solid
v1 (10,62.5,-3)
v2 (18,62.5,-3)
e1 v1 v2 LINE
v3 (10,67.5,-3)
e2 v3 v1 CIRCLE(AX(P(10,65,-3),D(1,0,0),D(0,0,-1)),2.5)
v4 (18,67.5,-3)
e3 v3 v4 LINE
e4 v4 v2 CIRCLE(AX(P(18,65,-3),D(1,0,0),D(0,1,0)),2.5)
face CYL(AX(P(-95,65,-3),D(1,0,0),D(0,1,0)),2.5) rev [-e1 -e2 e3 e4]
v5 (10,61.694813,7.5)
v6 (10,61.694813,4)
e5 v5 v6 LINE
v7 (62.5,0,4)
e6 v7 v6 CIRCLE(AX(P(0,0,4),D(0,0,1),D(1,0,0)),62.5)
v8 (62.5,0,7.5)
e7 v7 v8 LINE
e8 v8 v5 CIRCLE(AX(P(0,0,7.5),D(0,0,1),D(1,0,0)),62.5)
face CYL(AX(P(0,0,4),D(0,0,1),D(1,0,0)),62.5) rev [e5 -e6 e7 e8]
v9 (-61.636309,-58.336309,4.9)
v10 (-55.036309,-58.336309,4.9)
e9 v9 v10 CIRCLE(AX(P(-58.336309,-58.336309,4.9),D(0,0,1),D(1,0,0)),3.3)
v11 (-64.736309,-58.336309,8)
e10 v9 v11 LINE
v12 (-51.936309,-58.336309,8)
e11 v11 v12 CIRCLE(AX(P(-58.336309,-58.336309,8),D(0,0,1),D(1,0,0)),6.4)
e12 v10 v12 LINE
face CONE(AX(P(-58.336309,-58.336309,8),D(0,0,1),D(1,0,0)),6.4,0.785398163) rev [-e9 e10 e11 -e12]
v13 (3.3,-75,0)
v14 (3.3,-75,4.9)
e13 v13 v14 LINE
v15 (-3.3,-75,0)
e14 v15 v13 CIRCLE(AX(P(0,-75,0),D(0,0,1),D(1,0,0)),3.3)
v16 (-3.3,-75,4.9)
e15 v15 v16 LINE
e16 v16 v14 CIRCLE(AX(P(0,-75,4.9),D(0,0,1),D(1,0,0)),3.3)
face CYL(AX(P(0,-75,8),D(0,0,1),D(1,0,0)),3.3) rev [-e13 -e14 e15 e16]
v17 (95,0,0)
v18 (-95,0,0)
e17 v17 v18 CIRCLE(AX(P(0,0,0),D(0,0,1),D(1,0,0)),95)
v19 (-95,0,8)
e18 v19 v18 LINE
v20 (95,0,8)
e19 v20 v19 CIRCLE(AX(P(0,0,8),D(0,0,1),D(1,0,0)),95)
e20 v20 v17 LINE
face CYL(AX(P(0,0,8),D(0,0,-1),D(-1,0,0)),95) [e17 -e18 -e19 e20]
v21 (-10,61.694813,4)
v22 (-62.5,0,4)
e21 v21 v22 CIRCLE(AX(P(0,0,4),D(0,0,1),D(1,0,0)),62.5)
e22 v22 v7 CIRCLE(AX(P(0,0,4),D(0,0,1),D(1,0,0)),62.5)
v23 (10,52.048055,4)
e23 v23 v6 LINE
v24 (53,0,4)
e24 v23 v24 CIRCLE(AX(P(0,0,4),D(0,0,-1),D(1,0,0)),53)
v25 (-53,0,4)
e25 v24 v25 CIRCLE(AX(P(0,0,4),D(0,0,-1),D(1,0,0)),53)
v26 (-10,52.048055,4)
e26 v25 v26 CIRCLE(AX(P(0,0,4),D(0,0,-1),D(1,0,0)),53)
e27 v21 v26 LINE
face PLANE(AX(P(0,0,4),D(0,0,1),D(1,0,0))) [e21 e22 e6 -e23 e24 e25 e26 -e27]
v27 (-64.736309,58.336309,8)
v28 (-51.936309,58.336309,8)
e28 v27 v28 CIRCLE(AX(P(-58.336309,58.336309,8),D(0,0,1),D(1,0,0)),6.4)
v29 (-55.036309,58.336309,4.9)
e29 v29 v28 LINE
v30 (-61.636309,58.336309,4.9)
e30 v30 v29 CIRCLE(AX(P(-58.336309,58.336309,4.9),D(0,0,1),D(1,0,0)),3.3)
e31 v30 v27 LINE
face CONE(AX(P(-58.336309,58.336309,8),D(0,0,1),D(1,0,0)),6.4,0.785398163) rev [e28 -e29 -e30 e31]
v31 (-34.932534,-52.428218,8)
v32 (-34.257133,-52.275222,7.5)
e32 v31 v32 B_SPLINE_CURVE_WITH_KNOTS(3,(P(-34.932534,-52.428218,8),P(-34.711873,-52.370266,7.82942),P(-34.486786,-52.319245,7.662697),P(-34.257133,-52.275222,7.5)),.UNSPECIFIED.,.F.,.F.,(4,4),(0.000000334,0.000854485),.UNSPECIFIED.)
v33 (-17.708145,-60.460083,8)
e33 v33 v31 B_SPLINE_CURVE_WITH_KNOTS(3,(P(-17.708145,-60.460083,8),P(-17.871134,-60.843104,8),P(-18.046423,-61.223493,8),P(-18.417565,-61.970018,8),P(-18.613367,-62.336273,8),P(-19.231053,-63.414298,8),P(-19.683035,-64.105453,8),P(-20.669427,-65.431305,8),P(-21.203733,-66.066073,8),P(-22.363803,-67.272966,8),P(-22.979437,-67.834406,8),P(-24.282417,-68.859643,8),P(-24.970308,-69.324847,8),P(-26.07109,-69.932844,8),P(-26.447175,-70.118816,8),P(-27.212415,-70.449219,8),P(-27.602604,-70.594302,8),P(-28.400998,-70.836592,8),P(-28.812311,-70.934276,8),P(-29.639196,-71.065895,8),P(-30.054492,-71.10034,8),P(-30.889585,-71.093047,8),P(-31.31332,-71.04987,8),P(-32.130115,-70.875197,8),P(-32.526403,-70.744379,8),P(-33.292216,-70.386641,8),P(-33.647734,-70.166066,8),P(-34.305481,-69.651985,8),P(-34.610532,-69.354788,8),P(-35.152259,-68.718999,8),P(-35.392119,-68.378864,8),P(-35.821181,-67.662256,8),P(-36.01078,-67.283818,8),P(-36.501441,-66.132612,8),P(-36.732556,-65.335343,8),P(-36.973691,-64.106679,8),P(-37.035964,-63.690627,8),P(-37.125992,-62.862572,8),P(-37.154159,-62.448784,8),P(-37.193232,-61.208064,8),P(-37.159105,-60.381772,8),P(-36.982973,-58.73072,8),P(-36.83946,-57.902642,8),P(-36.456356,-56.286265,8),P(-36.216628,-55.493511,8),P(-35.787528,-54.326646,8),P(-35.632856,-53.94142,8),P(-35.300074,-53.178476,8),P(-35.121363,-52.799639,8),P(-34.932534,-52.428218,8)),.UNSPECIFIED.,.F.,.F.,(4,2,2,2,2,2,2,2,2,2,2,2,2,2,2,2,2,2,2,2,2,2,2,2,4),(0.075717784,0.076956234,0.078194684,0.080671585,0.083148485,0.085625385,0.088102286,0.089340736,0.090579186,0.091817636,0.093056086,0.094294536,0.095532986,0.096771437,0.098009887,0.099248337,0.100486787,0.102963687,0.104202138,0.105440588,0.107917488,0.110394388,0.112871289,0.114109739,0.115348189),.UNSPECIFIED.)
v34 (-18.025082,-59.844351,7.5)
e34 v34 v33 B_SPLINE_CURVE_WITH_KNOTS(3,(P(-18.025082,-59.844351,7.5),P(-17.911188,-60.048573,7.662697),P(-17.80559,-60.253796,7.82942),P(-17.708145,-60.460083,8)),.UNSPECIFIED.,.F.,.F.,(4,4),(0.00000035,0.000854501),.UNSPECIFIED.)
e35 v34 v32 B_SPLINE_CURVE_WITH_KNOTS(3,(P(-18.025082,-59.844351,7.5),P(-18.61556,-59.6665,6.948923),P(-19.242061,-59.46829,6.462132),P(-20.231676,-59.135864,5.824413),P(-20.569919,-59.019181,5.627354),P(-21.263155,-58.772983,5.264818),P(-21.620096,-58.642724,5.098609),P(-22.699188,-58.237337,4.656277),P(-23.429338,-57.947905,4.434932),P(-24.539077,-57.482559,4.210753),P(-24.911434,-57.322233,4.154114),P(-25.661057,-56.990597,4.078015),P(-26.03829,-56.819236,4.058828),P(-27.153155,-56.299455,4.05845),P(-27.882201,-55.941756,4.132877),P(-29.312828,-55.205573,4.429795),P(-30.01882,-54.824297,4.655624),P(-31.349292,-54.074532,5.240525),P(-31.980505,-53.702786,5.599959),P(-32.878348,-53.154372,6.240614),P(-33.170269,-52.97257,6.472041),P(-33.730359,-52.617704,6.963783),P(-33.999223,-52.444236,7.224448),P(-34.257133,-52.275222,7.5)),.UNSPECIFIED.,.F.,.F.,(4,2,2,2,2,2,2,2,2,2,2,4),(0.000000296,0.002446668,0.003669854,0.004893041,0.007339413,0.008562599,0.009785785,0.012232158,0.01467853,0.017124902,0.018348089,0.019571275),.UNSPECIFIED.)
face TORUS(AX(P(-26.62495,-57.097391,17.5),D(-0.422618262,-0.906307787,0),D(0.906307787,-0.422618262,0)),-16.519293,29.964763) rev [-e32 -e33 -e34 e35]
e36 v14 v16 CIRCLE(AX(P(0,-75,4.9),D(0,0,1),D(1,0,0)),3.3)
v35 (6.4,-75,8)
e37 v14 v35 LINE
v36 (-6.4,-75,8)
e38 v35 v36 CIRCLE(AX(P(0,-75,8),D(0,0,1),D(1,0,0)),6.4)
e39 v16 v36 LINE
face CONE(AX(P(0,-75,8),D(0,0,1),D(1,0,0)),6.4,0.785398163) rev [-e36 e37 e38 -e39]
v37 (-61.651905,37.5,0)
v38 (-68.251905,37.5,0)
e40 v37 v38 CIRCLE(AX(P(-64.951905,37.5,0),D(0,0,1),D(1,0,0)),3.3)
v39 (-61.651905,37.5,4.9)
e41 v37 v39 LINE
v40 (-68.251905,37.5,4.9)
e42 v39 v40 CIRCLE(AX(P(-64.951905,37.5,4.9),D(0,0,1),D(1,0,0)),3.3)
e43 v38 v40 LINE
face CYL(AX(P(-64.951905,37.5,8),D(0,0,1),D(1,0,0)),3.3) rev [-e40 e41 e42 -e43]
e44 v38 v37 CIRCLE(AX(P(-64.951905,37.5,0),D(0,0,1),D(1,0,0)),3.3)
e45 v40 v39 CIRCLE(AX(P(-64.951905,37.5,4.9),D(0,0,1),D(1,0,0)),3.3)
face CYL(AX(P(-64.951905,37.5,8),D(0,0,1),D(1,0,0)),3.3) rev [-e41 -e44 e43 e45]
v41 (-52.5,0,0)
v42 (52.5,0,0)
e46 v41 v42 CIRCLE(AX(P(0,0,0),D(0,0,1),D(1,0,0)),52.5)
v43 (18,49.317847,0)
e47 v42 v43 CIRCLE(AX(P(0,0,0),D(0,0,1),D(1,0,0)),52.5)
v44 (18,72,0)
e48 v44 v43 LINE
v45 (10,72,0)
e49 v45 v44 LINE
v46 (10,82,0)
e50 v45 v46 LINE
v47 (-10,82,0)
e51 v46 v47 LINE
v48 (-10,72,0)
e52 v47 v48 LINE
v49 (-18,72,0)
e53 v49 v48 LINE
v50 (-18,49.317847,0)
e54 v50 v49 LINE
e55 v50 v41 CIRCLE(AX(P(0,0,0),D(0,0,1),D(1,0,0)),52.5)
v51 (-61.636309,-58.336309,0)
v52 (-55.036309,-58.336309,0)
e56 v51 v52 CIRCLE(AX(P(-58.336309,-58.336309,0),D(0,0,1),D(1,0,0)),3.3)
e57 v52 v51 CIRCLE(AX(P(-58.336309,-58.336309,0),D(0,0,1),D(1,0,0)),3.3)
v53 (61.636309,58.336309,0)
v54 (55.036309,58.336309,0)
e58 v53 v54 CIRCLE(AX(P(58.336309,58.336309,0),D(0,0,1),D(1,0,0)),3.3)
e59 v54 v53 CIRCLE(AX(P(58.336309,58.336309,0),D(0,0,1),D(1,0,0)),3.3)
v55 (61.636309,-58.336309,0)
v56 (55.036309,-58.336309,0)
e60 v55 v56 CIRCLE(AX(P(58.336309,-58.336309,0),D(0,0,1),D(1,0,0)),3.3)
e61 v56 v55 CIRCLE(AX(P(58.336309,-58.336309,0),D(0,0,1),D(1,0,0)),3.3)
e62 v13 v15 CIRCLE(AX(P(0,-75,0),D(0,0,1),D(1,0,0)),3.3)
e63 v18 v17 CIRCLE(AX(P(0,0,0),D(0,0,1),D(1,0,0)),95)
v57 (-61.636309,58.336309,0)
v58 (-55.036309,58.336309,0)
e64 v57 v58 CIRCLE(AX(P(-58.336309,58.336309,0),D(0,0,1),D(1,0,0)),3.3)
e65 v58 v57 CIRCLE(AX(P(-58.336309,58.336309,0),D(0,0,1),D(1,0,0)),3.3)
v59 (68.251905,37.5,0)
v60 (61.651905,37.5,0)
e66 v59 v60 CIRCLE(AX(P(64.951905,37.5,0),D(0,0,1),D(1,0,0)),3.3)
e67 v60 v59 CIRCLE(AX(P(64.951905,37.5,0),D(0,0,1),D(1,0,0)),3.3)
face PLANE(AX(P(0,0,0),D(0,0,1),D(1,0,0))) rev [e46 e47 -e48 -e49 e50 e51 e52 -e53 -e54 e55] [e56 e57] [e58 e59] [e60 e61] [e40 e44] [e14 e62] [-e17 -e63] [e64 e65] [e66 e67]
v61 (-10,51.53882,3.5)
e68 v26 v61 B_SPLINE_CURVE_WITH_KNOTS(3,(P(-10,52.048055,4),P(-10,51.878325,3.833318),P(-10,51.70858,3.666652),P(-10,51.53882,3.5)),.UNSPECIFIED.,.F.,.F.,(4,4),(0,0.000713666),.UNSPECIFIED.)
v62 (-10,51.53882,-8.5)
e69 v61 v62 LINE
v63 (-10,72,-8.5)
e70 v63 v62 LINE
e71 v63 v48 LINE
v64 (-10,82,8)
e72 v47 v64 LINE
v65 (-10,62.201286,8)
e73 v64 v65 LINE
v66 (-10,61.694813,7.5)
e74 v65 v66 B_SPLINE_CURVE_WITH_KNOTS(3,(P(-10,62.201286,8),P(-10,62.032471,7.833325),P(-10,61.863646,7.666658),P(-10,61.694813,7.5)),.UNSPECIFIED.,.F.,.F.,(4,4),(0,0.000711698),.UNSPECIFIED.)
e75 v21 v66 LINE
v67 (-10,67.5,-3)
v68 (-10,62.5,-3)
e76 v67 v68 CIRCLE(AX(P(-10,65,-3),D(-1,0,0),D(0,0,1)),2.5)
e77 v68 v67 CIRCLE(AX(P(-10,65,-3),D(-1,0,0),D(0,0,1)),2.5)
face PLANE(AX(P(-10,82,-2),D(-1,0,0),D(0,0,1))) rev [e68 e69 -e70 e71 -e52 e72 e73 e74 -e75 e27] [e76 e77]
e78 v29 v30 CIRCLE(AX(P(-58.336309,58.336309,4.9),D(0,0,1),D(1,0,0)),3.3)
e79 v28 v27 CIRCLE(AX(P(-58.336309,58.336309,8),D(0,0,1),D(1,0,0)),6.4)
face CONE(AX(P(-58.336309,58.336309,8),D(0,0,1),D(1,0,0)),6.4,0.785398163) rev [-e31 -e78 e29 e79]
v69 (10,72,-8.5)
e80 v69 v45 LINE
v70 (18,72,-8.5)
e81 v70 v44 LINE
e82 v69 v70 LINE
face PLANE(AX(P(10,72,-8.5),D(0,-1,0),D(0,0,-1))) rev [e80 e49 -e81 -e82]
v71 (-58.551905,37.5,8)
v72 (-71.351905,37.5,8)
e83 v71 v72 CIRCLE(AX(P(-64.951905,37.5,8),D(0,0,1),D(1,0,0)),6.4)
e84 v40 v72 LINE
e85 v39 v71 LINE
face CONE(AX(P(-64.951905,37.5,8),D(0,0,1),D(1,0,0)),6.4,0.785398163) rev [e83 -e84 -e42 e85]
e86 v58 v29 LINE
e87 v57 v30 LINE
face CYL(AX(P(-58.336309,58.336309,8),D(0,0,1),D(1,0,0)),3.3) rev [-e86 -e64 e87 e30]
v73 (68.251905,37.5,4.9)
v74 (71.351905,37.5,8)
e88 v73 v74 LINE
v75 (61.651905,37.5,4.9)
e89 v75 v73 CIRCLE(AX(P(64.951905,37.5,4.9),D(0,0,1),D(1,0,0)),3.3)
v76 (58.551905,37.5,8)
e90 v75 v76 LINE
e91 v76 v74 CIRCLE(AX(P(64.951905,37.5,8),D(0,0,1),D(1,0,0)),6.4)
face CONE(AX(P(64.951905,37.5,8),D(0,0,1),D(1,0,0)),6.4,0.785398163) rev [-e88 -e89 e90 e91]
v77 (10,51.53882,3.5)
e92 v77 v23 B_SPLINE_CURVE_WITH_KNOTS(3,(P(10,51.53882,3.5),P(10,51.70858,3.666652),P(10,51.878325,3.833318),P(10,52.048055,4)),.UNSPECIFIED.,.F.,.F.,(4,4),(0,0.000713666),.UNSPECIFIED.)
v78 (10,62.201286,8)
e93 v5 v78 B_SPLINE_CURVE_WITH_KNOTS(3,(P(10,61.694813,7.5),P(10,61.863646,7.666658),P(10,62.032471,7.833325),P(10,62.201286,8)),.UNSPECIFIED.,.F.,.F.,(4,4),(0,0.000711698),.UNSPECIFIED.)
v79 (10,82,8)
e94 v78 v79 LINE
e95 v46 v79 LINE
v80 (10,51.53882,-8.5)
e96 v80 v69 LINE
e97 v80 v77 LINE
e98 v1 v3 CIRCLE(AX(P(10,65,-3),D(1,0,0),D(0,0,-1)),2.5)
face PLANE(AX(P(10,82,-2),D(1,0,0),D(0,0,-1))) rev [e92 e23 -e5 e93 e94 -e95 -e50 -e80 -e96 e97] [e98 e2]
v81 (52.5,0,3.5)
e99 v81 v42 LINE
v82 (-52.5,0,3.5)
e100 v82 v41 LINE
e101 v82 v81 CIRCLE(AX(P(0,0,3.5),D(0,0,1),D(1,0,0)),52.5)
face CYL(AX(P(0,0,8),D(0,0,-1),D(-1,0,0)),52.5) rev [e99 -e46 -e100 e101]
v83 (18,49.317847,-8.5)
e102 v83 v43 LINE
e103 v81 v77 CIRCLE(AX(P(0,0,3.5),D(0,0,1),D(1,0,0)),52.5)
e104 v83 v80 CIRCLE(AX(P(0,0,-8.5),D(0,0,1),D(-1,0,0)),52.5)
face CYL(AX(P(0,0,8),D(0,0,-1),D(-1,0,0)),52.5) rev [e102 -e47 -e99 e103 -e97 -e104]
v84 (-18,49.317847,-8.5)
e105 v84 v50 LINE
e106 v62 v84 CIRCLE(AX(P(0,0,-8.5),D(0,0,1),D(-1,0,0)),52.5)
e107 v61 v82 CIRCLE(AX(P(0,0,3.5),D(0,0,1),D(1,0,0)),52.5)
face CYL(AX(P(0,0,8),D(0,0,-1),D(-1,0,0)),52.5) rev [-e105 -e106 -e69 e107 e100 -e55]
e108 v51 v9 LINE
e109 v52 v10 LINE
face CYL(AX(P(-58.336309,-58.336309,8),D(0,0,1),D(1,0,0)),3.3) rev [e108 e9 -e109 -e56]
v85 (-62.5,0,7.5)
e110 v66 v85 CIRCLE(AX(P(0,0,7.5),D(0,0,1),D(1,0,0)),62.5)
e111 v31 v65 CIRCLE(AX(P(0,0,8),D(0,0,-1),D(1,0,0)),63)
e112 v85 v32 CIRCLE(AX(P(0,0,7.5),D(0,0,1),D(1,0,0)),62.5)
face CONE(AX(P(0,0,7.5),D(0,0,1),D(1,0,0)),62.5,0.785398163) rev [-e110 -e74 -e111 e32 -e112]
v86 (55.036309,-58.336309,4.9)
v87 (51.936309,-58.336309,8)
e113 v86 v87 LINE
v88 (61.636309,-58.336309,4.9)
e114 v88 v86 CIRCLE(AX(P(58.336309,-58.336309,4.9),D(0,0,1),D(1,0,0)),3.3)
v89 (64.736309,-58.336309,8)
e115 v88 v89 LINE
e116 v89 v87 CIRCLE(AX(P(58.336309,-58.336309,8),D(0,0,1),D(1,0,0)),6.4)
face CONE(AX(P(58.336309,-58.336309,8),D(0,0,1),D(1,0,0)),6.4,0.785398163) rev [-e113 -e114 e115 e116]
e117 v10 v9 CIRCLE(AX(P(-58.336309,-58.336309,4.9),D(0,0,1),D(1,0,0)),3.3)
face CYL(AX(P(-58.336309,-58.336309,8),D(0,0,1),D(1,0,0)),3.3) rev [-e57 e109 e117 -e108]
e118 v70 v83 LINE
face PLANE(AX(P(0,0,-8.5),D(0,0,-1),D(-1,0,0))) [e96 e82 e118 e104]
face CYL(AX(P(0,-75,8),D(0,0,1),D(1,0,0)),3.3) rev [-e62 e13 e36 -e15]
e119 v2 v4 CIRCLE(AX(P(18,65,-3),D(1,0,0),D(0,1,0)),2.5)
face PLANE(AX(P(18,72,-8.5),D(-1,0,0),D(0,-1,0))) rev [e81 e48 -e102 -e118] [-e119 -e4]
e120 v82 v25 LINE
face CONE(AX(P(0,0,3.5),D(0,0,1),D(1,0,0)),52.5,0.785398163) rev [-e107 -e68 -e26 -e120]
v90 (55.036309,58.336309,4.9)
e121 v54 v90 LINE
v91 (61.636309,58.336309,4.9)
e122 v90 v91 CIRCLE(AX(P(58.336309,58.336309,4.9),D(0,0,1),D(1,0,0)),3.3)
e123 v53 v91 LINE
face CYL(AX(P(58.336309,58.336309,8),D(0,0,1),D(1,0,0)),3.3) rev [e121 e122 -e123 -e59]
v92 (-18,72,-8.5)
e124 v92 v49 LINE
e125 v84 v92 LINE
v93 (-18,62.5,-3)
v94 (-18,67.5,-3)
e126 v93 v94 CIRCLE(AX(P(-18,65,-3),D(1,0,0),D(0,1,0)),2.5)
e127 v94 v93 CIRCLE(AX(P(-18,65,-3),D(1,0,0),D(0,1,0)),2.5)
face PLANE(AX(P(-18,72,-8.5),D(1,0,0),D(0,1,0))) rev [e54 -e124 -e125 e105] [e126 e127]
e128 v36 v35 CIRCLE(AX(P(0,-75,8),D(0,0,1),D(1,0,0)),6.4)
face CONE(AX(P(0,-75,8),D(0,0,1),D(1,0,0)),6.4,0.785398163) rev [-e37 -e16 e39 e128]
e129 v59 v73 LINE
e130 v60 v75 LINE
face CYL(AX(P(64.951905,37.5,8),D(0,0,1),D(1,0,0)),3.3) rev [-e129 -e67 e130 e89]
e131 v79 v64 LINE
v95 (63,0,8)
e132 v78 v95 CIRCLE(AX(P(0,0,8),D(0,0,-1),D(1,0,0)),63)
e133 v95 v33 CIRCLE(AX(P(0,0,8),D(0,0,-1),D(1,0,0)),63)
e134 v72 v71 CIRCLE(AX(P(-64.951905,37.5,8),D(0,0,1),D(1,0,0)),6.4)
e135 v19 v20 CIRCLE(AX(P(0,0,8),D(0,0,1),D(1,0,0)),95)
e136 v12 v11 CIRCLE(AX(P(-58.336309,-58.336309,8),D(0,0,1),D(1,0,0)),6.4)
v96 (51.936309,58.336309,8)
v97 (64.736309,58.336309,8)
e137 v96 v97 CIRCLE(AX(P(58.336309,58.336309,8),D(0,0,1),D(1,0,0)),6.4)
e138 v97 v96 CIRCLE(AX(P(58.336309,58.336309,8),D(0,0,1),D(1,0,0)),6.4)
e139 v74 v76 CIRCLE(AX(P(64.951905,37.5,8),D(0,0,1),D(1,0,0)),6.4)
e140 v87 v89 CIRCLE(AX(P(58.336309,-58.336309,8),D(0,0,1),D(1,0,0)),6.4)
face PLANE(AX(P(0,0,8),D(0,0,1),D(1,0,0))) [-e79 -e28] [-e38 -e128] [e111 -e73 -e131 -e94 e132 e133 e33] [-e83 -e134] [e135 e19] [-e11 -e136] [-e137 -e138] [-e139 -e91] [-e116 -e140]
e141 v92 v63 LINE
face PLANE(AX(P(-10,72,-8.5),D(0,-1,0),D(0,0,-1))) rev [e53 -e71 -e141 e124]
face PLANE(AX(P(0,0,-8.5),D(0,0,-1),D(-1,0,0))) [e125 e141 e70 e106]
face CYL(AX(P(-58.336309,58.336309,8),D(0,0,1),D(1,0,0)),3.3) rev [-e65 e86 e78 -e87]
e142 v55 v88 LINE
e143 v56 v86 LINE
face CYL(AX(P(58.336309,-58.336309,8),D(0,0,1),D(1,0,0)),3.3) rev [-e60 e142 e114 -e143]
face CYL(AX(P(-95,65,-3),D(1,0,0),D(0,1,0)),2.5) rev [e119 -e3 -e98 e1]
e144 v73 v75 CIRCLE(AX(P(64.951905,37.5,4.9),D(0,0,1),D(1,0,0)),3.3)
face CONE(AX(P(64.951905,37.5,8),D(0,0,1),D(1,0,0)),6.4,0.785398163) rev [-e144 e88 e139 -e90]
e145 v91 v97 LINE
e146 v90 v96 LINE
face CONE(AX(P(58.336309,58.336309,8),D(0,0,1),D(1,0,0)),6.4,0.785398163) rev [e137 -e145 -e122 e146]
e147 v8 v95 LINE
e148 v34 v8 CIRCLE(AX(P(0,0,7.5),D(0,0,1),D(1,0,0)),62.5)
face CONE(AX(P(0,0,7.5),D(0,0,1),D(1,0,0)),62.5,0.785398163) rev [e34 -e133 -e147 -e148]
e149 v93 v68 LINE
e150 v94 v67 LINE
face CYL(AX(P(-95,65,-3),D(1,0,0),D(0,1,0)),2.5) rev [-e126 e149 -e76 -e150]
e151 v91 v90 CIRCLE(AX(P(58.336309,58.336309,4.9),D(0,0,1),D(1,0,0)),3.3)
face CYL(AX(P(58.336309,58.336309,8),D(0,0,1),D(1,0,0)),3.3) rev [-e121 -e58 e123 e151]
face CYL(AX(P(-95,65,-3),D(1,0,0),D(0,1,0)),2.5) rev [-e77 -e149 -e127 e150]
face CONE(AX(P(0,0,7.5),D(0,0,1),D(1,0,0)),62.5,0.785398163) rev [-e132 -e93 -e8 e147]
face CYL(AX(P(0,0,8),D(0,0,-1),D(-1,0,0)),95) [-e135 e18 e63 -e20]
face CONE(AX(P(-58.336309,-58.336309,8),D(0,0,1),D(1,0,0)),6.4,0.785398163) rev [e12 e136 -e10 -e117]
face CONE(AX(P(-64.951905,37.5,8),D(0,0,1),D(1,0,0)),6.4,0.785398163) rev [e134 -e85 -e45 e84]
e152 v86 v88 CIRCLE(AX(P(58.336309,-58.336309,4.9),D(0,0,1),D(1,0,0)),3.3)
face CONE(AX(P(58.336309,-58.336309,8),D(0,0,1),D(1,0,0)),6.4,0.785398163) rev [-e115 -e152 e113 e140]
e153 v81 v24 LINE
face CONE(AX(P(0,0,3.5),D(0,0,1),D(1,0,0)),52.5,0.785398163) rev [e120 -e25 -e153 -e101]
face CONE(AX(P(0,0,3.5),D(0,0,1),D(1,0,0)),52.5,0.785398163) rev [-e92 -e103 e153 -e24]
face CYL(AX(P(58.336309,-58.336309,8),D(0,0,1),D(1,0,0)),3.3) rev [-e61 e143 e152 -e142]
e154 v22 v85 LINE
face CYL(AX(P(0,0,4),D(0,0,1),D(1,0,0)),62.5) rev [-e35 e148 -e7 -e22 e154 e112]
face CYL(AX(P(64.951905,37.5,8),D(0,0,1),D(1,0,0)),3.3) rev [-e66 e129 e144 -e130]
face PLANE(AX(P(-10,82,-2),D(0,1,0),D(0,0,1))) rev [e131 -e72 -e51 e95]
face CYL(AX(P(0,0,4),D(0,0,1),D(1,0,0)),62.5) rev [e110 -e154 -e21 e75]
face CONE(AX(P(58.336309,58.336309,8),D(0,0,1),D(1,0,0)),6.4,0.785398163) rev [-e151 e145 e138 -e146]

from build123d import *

# Parameters (mm, degrees)
SKETCH_1_R               = 95
SKETCH_1_R_2             = 52.5
EXTRUDE_1_DEPTH          = 8
SKETCH_3_R               = 62.5
CUT_EXTRUDE_1_DEPTH      = 4
PATTERN_CIRCULAR_1_COUNT = 3
PATTERN_CIRCULAR_2_COUNT = 4
SKETCH_7_W               = 20
SKETCH_7_H               = 39
CUT_EXTRUDE_2_DEPTH      = 10
EXTRUDE_START            = 8.5
EXTRUDE_2_DEPTH          = 8.5
SKETCH_9_R               = 2.5
CUT_EXTRUDE_3_DEPTH      = 148.87241122
CHAMFER_1_SIZE           = 0.5


with BuildPart() as part:
    # 草图1 → 凸台-拉伸1 (new body)
    with BuildSketch(Plane.XY):
        Circle(SKETCH_1_R)
        Circle(SKETCH_1_R_2, mode=Mode.SUBTRACT)
    extrude(amount=EXTRUDE_1_DEPTH)

    # 草图3 → 切除-拉伸1 (cut)
    with BuildSketch(Plane.XY.offset(8)):
        Circle(SKETCH_3_R)
    extrude(amount=-CUT_EXTRUDE_1_DEPTH, mode=Mode.SUBTRACT)

    # 草图5 → 打孔尺寸(%根据)内六角花形半沉头螺钉的类型1 (revolve, cut)
    with BuildSketch(Plane(origin=(0, -75, 8), x_dir=(0, -1, 0), z_dir=(1, 0, 0))):
        Polygon((0, 0), (0, 26.482840043), (3.3, 24.5), (3.3, 3.1), (6.4, 0), align=None)
    hole_wizard_1 = revolve(axis=Axis((0, -75, 14.35), (0, 0, -1)), mode=Mode.SUBTRACT)

    # 草图6 → 打孔尺寸(%根据)内六角花形半沉头螺钉的类型2 (revolve, cut)
    with BuildSketch(Plane(origin=(-58.336309448, -58.336309448, 8), x_dir=(0, -1, 0), z_dir=(1, 0, 0))):
        Polygon((0, 0), (0, 26.482840043), (3.3, 24.5), (3.3, 3.1), (6.4, 0), align=None)
    hole_wizard_2 = revolve(axis=Axis((-58.336309448, -58.336309448, 14.35), (0, 0, -1)), mode=Mode.SUBTRACT)

    # 阵列(圆周)1: 打孔尺寸(%根据)内六角花形半沉头螺钉的类型1 ×3 about axis
    pattern_circular_1_axis = Axis((0, 0, 0), (0, 0, 1))
    for i in range(1, PATTERN_CIRCULAR_1_COUNT):
        add(hole_wizard_1.rotate(pattern_circular_1_axis, i * 360 / PATTERN_CIRCULAR_1_COUNT), mode=Mode.SUBTRACT)

    # 阵列(圆周)2: 打孔尺寸(%根据)内六角花形半沉头螺钉的类型2 ×4 about axis
    pattern_circular_2_axis = Axis((0, 0, 0), (0, 0, 1))
    for i in range(1, PATTERN_CIRCULAR_2_COUNT):
        add(hole_wizard_2.rotate(pattern_circular_2_axis, i * 360 / PATTERN_CIRCULAR_2_COUNT), mode=Mode.SUBTRACT)

    # 草图7 → 切除-拉伸2 (cut)
    with BuildSketch(Plane.XY.offset(8)):
        with Locations((0, 62.5)):
            Rectangle(SKETCH_7_W, SKETCH_7_H)
    extrude(amount=-CUT_EXTRUDE_2_DEPTH, mode=Mode.SUBTRACT)

    # 草图8 → 凸台-拉伸2 (add)
    with BuildSketch(Plane(origin=(0, 0, 0), x_dir=(-1, 0, 0), z_dir=(0, 0, -1)).offset(EXTRUDE_START)):
        with BuildLine():
            Line((10, 72), (18, 72))
            Line((18, 72), (18, 49.317846668))
            ThreePointArc((18, 49.317846668), (14.04397312, 50.586725719), (10, 51.53882032))
            Line((10, 51.53882032), (10, 72))
        make_face()
        with BuildLine():
            Line((-10, 72), (-18, 72))
            Line((-18, 72), (-18, 49.317846668))
            ThreePointArc((-18, 49.317846668), (-14.04397312, 50.586725719), (-10, 51.53882032))
            Line((-10, 51.53882032), (-10, 72))
        make_face()
    extrude(amount=-EXTRUDE_2_DEPTH)

    # 草图9 → 切除-拉伸3 (cut, through all)
    with BuildSketch(Plane(origin=(18, 0, 0), x_dir=(0, 0, -1), z_dir=(1, 0, 0))):
        with Locations(Location((3, 65, 0), (0, 0, 90))):
            Circle(SKETCH_9_R)
    extrude(amount=-CUT_EXTRUDE_3_DEPTH, mode=Mode.SUBTRACT)

    # 倒角1
    chamfer_1_edges = [part.edges().sort_by_distance(p)[0] for p in [
        (0, -52.5, 4),
        (0, -62.5, 8),
    ]]
    chamfer(chamfer_1_edges, length=CHAMFER_1_SIZE)

    # 草图12 → 切除-旋转1 (revolve, cut)
    with BuildSketch(Plane(origin=(0, 0, 0), x_dir=(0, 0, -1), z_dir=(-0.9063077870366526, 0.42261826174069383, 0))):
        with BuildLine():
            Line((-17.5, 88), (-17.5, 38))
            ThreePointArc((-17.5, 38), (-4.054529719, 63), (-17.5, 88))
        make_face()
    revolve(axis=Axis((-37.190407033, -79.755085259, 17.5), (0.4226182617406939, 0.9063077870366525, 0)), mode=Mode.SUBTRACT)


solid = part.part
